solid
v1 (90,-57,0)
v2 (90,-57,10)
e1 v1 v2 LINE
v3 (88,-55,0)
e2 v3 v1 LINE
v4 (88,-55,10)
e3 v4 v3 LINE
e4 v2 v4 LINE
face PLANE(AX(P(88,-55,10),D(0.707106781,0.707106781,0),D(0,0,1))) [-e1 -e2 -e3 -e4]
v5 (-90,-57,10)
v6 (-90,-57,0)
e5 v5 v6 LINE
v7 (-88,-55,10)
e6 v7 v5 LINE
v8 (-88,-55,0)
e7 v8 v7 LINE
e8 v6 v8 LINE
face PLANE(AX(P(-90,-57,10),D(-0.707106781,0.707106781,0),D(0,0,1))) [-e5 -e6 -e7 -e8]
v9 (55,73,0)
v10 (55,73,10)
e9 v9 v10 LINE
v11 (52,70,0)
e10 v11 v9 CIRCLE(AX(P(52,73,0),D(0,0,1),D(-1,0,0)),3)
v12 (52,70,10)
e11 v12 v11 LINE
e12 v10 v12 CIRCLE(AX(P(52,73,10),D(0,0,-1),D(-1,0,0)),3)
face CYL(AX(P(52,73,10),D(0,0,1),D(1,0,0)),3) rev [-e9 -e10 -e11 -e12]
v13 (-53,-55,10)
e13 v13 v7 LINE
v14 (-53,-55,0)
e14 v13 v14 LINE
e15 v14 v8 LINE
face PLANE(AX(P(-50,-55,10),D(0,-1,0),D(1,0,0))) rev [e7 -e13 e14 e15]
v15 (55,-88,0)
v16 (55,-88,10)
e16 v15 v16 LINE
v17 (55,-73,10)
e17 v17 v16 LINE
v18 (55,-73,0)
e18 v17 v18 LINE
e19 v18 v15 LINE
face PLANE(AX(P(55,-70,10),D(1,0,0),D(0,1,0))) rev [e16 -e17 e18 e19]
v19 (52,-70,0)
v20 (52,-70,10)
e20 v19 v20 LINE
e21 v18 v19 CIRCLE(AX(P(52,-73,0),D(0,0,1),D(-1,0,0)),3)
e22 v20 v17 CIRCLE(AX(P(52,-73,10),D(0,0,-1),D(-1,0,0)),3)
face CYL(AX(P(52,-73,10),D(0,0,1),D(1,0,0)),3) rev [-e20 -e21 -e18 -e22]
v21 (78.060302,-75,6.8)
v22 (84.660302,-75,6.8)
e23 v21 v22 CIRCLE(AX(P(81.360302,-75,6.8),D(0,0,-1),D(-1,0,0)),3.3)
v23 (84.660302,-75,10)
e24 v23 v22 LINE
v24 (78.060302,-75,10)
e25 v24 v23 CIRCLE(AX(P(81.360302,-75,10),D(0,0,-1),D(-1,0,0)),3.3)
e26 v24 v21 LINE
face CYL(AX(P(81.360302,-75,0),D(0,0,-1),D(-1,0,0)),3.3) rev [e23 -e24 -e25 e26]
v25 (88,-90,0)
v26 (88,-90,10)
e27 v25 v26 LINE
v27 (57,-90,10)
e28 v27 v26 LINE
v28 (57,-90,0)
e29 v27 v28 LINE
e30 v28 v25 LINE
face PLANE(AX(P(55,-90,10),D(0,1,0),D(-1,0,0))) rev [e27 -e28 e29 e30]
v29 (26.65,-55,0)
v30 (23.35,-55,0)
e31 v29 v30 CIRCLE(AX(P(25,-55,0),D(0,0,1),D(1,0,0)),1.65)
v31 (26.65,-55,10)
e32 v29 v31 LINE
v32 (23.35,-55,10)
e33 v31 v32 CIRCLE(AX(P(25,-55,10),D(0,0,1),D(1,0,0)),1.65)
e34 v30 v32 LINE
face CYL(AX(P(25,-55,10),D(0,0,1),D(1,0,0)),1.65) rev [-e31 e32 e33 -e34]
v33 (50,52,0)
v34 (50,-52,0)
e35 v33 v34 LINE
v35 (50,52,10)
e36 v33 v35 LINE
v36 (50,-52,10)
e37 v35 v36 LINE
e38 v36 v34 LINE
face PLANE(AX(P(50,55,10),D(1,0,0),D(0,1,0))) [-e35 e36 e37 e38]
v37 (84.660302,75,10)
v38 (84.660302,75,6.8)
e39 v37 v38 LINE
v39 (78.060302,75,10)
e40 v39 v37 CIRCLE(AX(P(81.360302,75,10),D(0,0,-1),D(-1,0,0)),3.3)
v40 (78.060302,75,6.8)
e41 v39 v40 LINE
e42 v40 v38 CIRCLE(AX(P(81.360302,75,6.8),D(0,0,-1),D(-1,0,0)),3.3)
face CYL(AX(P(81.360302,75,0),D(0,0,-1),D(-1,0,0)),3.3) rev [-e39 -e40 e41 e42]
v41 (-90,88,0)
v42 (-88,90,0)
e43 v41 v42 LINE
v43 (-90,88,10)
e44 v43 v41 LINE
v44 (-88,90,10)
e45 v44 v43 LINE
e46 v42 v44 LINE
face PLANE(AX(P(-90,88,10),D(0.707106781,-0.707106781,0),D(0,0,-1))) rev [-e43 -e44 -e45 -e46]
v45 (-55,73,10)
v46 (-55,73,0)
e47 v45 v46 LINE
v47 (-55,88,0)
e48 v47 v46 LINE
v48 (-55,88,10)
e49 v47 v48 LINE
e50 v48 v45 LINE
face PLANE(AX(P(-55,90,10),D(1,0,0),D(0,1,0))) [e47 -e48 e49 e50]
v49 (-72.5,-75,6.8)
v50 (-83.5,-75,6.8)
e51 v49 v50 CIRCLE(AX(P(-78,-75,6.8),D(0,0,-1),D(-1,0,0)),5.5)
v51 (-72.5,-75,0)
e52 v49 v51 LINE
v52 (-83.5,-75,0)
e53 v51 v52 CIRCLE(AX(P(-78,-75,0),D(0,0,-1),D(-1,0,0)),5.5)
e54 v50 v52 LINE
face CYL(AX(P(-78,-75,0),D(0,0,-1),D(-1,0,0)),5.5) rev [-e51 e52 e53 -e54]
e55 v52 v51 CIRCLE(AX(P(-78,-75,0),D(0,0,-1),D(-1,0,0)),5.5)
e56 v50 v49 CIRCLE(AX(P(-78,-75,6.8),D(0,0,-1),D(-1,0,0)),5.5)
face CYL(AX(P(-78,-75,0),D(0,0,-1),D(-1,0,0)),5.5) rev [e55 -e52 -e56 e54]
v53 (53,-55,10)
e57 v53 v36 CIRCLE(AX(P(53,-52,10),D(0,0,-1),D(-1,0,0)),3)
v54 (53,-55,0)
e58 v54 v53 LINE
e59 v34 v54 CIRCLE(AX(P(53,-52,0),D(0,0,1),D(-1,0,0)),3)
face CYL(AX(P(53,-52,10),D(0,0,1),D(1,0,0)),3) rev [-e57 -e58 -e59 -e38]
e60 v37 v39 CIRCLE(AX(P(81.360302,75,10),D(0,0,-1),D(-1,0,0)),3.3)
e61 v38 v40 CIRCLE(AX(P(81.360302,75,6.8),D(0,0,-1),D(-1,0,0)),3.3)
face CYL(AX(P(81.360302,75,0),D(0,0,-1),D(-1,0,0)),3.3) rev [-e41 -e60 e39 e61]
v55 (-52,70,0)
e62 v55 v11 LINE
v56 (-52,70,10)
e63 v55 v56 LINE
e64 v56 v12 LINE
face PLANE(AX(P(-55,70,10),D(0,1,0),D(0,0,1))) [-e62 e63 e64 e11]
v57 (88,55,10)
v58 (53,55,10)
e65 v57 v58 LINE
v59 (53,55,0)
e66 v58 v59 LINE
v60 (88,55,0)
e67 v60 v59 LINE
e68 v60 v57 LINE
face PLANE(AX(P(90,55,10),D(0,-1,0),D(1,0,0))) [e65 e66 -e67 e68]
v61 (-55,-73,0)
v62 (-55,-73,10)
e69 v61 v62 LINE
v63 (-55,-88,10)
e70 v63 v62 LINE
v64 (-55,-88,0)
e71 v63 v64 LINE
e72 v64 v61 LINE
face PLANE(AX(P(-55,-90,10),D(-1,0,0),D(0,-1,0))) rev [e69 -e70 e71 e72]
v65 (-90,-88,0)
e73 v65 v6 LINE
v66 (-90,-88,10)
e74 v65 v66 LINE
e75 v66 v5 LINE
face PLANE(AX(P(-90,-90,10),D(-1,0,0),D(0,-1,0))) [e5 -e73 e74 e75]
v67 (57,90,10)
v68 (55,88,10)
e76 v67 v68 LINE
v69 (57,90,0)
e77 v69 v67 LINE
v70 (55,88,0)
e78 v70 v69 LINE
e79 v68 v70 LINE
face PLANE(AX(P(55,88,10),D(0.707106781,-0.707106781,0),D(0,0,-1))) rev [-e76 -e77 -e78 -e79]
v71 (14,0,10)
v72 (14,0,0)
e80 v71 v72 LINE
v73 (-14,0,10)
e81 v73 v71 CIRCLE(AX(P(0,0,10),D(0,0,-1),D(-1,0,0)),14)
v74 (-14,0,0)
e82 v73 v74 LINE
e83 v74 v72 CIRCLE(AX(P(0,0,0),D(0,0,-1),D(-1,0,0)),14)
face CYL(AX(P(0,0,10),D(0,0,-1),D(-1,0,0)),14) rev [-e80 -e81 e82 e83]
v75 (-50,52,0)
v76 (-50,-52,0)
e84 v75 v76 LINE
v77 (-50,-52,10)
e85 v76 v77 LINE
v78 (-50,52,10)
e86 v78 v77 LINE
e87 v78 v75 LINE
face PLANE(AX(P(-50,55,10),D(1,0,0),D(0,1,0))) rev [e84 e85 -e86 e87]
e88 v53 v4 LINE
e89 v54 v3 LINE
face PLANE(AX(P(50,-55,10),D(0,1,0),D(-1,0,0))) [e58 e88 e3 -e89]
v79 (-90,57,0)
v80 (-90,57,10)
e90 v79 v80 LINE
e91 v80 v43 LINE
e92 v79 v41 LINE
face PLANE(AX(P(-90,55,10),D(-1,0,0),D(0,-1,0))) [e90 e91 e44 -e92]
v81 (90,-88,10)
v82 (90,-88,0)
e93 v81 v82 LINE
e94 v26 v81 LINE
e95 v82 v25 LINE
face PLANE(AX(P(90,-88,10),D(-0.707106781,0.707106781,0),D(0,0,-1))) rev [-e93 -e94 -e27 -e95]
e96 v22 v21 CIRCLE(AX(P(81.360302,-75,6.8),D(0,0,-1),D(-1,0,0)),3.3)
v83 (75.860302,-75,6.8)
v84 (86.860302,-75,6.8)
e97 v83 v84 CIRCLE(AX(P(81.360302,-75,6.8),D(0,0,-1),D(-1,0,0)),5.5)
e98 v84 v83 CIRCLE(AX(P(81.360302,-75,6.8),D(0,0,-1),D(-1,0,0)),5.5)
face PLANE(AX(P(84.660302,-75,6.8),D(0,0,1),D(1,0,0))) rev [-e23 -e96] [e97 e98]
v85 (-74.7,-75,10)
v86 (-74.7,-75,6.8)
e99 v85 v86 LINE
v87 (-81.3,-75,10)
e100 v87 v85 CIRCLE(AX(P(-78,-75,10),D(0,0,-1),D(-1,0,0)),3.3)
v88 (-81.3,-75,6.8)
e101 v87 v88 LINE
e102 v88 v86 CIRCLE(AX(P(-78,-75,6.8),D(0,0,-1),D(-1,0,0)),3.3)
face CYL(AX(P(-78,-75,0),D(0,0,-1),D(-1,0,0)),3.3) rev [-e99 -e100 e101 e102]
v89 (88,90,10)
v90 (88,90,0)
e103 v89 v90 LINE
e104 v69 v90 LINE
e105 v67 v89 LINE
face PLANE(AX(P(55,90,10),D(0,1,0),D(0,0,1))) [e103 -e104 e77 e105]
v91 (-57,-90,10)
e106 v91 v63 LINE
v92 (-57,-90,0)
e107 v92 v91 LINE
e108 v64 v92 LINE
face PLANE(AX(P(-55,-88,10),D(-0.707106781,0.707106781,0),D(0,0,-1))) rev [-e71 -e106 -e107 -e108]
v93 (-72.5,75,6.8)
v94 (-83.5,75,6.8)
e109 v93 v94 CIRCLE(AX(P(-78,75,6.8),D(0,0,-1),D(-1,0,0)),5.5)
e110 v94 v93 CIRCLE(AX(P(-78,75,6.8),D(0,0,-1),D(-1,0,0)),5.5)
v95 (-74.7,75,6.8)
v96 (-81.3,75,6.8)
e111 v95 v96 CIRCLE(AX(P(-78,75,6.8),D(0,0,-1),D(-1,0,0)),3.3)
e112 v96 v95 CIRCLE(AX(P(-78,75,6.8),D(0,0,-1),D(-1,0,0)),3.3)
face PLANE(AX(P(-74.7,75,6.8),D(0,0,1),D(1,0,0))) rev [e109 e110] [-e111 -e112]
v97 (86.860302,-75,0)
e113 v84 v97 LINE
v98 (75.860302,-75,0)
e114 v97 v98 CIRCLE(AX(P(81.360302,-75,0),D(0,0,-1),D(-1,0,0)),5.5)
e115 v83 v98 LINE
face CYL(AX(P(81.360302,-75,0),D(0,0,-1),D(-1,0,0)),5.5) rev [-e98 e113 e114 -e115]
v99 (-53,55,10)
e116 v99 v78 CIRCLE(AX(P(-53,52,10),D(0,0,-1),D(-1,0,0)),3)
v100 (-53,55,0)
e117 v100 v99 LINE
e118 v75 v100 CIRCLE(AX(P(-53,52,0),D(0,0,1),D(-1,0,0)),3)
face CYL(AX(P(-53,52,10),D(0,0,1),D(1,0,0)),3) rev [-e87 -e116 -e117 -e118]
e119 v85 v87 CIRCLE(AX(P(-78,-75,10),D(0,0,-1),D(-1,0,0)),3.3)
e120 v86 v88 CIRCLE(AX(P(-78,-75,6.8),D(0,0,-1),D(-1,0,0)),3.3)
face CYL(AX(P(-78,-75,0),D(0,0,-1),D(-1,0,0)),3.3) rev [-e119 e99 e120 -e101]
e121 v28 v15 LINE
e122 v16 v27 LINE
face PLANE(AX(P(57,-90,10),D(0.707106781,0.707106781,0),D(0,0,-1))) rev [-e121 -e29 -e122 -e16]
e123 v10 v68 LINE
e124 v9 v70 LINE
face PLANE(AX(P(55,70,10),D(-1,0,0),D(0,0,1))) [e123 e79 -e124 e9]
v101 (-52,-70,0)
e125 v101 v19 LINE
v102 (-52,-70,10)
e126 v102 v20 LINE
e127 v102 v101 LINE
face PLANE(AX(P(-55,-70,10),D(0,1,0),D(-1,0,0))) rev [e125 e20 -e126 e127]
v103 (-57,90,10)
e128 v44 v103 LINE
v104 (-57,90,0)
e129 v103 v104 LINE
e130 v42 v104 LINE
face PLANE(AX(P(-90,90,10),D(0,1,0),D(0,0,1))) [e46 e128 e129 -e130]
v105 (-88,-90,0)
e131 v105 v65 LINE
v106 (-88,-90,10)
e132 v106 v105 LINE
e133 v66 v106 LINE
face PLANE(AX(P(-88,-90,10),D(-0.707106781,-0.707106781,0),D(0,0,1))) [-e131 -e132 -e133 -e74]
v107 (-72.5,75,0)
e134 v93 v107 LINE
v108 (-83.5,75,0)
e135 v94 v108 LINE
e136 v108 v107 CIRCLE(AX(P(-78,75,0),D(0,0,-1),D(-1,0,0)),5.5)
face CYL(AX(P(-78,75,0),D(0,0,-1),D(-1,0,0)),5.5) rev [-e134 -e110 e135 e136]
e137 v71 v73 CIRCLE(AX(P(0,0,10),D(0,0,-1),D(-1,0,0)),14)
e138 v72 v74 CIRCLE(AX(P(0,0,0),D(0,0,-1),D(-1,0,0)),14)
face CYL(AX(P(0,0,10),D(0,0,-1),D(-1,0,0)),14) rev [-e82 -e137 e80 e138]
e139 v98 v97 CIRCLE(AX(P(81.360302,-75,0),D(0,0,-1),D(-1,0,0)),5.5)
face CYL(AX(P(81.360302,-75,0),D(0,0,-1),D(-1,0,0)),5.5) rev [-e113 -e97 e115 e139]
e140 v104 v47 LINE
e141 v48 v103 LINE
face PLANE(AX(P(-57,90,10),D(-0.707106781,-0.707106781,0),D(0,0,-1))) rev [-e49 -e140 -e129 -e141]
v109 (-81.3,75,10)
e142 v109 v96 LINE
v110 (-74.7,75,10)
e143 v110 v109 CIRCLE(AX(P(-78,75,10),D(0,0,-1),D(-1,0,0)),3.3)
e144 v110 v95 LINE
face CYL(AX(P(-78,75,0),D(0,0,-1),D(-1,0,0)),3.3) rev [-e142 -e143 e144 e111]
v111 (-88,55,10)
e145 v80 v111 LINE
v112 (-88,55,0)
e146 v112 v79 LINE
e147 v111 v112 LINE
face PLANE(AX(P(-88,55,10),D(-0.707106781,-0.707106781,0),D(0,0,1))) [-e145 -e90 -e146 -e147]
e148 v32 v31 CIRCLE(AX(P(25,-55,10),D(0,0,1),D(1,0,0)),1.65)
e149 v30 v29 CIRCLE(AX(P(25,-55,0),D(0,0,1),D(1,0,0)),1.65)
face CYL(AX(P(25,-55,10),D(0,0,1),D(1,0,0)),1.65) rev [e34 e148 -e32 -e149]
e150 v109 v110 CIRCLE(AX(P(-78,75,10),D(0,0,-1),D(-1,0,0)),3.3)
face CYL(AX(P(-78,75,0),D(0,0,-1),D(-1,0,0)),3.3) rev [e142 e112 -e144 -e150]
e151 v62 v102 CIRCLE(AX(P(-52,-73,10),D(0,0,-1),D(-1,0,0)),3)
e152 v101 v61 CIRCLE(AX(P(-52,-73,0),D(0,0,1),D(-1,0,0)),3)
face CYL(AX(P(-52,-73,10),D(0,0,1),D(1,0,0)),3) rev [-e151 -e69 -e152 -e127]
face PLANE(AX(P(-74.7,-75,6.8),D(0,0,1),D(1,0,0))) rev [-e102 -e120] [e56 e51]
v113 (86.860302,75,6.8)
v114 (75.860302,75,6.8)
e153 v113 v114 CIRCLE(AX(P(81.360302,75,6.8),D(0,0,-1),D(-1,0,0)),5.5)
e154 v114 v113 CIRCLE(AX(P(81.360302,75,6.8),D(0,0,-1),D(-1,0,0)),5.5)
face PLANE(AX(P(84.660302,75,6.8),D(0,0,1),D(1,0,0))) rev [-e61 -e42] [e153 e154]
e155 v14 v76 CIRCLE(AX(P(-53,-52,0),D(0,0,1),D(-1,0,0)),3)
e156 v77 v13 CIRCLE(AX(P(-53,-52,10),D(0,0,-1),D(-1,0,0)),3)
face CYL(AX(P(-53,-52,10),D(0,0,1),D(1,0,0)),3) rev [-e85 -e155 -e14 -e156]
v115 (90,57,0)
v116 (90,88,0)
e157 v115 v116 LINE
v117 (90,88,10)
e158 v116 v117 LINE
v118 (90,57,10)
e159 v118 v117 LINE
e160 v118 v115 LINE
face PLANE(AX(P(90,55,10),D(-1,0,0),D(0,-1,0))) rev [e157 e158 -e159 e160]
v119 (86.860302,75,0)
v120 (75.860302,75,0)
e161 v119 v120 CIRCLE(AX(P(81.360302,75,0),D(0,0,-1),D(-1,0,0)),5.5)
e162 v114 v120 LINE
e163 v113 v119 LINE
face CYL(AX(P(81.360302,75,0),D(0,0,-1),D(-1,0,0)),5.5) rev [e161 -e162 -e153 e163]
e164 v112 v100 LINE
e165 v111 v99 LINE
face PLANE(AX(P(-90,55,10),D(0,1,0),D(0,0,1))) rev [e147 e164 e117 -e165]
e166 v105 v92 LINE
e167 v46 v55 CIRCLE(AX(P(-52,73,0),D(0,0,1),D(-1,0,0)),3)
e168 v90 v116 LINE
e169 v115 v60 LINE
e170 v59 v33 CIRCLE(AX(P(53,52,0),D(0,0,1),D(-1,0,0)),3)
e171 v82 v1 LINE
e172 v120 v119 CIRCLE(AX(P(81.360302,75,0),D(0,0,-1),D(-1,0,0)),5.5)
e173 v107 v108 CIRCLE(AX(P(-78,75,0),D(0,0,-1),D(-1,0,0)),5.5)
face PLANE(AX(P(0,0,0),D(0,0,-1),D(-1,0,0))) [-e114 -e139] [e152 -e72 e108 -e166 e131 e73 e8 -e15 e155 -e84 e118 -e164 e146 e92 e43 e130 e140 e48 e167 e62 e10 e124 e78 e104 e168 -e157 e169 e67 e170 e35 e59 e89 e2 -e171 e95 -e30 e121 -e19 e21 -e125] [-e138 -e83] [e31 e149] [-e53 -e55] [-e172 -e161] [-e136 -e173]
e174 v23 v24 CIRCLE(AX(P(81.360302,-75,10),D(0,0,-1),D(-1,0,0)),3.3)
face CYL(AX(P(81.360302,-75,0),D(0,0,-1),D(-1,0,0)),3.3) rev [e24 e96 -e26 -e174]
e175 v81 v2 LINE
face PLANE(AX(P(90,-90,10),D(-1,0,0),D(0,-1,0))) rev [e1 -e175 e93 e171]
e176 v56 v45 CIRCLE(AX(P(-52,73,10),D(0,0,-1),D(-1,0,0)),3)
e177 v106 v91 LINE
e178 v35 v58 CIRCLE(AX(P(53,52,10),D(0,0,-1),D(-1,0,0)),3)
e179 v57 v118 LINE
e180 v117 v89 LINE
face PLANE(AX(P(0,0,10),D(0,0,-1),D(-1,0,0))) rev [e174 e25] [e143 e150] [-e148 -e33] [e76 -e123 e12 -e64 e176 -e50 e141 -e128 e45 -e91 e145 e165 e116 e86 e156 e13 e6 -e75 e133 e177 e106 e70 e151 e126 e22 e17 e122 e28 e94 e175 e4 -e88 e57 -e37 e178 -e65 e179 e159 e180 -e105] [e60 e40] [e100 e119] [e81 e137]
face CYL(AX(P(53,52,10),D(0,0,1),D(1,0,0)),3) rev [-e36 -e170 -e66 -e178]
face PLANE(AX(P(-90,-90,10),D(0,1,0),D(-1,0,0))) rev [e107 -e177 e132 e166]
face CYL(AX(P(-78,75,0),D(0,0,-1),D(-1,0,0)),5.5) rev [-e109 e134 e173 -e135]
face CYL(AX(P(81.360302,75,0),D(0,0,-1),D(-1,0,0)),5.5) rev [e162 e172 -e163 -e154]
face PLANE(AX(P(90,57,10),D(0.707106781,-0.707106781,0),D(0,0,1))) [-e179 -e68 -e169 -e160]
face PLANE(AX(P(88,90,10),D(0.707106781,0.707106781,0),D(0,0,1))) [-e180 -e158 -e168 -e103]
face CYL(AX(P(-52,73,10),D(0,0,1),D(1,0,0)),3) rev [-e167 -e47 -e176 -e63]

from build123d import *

# Parameters (mm, degrees)
BOSS_EXTRUDE1_DEPTH                                  = 10
SKETCH2_R                                            = 14
CUT_EXTRUDE1_DEPTH                                   = 128.671453348
M4_TAPPED_HOLE1_D                                    = 3.3
CBORE_FOR_M6_HEXAGON_SOCKET_HEAD_CAP_SCR_D           = 6.6
CBORE_FOR_M6_HEXAGON_SOCKET_HEAD_CAP_SCR_CBORE_D     = 11
CBORE_FOR_M6_HEXAGON_SOCKET_HEAD_CAP_SCR_CBORE_DEPTH = 6.8
CHAMFER1_SIZE                                        = 2
FILLET1_R                                            = 3


with BuildPart() as part:
    # Sketch1 → Boss-Extrude1 (new body)
    with BuildSketch(Plane.XY):
        Polygon((-90, 55), (-50, 55), (-50, -55), (-90, -55), (-90, -90), (-55, -90), (-55, -70), (55, -70), (55, -90), (90, -90), (90, -55), (50, -55), (50, 55), (90, 55), (90, 90), (55, 90), (55, 70), (-55, 70), (-55, 90), (-90, 90), align=None)
    extrude(amount=BOSS_EXTRUDE1_DEPTH)

    # Sketch2 → Cut-Extrude1 (cut, through all)
    with BuildSketch(Plane(origin=(0, 0, 0), x_dir=(-1, 0, 0), z_dir=(0, 0, -1))):
        Circle(SKETCH2_R)
    extrude(amount=-CUT_EXTRUDE1_DEPTH, mode=Mode.SUBTRACT)

    # M4 Tapped Hole1 (through all)
    with Locations(Plane.XY.offset(10)):
        with Locations((25, -55)):
            Hole(M4_TAPPED_HOLE1_D / 2)

    # CBORE for M6 Hexagon socket head cap screws1 (through all)
    with Locations(Plane(origin=(0, 0, 0), x_dir=(-1, 0, 0), z_dir=(0, 0, -1))):
        with Locations((78, -75), (78, 75), (-81.36030205, 75), (-81.36030205, -75)):
            CounterBoreHole(CBORE_FOR_M6_HEXAGON_SOCKET_HEAD_CAP_SCR_D / 2, CBORE_FOR_M6_HEXAGON_SOCKET_HEAD_CAP_SCR_CBORE_D / 2, CBORE_FOR_M6_HEXAGON_SOCKET_HEAD_CAP_SCR_CBORE_DEPTH)

    # Chamfer1
    chamfer1_edges = [part.edges().sort_by_distance(p)[0] for p in [
        (-90, 55, 5),
        (-90, 90, 5),
        (-55, 90, 5),
        (55, 90, 5),
        (90, 90, 5),
        (90, 55, 5),
        (90, -55, 5),
        (90, -90, 5),
        (55, -90, 5),
        (-55, -90, 5),
        (-90, -90, 5),
        (-90, -55, 5),
    ]]
    chamfer(chamfer1_edges, length=CHAMFER1_SIZE)

    # Fillet1
    fillet1_edges = [part.edges().sort_by_distance(p)[0] for p in [
        (-55, 70, 5),
        (55, 70, 5),
        (50, 55, 5),
        (50, -55, 5),
        (55, -70, 5),
        (-55, -70, 5),
        (-50, -55, 5),
        (-50, 55, 5),
    ]]
    fillet(fillet1_edges, radius=FILLET1_R)


solid = part.part
